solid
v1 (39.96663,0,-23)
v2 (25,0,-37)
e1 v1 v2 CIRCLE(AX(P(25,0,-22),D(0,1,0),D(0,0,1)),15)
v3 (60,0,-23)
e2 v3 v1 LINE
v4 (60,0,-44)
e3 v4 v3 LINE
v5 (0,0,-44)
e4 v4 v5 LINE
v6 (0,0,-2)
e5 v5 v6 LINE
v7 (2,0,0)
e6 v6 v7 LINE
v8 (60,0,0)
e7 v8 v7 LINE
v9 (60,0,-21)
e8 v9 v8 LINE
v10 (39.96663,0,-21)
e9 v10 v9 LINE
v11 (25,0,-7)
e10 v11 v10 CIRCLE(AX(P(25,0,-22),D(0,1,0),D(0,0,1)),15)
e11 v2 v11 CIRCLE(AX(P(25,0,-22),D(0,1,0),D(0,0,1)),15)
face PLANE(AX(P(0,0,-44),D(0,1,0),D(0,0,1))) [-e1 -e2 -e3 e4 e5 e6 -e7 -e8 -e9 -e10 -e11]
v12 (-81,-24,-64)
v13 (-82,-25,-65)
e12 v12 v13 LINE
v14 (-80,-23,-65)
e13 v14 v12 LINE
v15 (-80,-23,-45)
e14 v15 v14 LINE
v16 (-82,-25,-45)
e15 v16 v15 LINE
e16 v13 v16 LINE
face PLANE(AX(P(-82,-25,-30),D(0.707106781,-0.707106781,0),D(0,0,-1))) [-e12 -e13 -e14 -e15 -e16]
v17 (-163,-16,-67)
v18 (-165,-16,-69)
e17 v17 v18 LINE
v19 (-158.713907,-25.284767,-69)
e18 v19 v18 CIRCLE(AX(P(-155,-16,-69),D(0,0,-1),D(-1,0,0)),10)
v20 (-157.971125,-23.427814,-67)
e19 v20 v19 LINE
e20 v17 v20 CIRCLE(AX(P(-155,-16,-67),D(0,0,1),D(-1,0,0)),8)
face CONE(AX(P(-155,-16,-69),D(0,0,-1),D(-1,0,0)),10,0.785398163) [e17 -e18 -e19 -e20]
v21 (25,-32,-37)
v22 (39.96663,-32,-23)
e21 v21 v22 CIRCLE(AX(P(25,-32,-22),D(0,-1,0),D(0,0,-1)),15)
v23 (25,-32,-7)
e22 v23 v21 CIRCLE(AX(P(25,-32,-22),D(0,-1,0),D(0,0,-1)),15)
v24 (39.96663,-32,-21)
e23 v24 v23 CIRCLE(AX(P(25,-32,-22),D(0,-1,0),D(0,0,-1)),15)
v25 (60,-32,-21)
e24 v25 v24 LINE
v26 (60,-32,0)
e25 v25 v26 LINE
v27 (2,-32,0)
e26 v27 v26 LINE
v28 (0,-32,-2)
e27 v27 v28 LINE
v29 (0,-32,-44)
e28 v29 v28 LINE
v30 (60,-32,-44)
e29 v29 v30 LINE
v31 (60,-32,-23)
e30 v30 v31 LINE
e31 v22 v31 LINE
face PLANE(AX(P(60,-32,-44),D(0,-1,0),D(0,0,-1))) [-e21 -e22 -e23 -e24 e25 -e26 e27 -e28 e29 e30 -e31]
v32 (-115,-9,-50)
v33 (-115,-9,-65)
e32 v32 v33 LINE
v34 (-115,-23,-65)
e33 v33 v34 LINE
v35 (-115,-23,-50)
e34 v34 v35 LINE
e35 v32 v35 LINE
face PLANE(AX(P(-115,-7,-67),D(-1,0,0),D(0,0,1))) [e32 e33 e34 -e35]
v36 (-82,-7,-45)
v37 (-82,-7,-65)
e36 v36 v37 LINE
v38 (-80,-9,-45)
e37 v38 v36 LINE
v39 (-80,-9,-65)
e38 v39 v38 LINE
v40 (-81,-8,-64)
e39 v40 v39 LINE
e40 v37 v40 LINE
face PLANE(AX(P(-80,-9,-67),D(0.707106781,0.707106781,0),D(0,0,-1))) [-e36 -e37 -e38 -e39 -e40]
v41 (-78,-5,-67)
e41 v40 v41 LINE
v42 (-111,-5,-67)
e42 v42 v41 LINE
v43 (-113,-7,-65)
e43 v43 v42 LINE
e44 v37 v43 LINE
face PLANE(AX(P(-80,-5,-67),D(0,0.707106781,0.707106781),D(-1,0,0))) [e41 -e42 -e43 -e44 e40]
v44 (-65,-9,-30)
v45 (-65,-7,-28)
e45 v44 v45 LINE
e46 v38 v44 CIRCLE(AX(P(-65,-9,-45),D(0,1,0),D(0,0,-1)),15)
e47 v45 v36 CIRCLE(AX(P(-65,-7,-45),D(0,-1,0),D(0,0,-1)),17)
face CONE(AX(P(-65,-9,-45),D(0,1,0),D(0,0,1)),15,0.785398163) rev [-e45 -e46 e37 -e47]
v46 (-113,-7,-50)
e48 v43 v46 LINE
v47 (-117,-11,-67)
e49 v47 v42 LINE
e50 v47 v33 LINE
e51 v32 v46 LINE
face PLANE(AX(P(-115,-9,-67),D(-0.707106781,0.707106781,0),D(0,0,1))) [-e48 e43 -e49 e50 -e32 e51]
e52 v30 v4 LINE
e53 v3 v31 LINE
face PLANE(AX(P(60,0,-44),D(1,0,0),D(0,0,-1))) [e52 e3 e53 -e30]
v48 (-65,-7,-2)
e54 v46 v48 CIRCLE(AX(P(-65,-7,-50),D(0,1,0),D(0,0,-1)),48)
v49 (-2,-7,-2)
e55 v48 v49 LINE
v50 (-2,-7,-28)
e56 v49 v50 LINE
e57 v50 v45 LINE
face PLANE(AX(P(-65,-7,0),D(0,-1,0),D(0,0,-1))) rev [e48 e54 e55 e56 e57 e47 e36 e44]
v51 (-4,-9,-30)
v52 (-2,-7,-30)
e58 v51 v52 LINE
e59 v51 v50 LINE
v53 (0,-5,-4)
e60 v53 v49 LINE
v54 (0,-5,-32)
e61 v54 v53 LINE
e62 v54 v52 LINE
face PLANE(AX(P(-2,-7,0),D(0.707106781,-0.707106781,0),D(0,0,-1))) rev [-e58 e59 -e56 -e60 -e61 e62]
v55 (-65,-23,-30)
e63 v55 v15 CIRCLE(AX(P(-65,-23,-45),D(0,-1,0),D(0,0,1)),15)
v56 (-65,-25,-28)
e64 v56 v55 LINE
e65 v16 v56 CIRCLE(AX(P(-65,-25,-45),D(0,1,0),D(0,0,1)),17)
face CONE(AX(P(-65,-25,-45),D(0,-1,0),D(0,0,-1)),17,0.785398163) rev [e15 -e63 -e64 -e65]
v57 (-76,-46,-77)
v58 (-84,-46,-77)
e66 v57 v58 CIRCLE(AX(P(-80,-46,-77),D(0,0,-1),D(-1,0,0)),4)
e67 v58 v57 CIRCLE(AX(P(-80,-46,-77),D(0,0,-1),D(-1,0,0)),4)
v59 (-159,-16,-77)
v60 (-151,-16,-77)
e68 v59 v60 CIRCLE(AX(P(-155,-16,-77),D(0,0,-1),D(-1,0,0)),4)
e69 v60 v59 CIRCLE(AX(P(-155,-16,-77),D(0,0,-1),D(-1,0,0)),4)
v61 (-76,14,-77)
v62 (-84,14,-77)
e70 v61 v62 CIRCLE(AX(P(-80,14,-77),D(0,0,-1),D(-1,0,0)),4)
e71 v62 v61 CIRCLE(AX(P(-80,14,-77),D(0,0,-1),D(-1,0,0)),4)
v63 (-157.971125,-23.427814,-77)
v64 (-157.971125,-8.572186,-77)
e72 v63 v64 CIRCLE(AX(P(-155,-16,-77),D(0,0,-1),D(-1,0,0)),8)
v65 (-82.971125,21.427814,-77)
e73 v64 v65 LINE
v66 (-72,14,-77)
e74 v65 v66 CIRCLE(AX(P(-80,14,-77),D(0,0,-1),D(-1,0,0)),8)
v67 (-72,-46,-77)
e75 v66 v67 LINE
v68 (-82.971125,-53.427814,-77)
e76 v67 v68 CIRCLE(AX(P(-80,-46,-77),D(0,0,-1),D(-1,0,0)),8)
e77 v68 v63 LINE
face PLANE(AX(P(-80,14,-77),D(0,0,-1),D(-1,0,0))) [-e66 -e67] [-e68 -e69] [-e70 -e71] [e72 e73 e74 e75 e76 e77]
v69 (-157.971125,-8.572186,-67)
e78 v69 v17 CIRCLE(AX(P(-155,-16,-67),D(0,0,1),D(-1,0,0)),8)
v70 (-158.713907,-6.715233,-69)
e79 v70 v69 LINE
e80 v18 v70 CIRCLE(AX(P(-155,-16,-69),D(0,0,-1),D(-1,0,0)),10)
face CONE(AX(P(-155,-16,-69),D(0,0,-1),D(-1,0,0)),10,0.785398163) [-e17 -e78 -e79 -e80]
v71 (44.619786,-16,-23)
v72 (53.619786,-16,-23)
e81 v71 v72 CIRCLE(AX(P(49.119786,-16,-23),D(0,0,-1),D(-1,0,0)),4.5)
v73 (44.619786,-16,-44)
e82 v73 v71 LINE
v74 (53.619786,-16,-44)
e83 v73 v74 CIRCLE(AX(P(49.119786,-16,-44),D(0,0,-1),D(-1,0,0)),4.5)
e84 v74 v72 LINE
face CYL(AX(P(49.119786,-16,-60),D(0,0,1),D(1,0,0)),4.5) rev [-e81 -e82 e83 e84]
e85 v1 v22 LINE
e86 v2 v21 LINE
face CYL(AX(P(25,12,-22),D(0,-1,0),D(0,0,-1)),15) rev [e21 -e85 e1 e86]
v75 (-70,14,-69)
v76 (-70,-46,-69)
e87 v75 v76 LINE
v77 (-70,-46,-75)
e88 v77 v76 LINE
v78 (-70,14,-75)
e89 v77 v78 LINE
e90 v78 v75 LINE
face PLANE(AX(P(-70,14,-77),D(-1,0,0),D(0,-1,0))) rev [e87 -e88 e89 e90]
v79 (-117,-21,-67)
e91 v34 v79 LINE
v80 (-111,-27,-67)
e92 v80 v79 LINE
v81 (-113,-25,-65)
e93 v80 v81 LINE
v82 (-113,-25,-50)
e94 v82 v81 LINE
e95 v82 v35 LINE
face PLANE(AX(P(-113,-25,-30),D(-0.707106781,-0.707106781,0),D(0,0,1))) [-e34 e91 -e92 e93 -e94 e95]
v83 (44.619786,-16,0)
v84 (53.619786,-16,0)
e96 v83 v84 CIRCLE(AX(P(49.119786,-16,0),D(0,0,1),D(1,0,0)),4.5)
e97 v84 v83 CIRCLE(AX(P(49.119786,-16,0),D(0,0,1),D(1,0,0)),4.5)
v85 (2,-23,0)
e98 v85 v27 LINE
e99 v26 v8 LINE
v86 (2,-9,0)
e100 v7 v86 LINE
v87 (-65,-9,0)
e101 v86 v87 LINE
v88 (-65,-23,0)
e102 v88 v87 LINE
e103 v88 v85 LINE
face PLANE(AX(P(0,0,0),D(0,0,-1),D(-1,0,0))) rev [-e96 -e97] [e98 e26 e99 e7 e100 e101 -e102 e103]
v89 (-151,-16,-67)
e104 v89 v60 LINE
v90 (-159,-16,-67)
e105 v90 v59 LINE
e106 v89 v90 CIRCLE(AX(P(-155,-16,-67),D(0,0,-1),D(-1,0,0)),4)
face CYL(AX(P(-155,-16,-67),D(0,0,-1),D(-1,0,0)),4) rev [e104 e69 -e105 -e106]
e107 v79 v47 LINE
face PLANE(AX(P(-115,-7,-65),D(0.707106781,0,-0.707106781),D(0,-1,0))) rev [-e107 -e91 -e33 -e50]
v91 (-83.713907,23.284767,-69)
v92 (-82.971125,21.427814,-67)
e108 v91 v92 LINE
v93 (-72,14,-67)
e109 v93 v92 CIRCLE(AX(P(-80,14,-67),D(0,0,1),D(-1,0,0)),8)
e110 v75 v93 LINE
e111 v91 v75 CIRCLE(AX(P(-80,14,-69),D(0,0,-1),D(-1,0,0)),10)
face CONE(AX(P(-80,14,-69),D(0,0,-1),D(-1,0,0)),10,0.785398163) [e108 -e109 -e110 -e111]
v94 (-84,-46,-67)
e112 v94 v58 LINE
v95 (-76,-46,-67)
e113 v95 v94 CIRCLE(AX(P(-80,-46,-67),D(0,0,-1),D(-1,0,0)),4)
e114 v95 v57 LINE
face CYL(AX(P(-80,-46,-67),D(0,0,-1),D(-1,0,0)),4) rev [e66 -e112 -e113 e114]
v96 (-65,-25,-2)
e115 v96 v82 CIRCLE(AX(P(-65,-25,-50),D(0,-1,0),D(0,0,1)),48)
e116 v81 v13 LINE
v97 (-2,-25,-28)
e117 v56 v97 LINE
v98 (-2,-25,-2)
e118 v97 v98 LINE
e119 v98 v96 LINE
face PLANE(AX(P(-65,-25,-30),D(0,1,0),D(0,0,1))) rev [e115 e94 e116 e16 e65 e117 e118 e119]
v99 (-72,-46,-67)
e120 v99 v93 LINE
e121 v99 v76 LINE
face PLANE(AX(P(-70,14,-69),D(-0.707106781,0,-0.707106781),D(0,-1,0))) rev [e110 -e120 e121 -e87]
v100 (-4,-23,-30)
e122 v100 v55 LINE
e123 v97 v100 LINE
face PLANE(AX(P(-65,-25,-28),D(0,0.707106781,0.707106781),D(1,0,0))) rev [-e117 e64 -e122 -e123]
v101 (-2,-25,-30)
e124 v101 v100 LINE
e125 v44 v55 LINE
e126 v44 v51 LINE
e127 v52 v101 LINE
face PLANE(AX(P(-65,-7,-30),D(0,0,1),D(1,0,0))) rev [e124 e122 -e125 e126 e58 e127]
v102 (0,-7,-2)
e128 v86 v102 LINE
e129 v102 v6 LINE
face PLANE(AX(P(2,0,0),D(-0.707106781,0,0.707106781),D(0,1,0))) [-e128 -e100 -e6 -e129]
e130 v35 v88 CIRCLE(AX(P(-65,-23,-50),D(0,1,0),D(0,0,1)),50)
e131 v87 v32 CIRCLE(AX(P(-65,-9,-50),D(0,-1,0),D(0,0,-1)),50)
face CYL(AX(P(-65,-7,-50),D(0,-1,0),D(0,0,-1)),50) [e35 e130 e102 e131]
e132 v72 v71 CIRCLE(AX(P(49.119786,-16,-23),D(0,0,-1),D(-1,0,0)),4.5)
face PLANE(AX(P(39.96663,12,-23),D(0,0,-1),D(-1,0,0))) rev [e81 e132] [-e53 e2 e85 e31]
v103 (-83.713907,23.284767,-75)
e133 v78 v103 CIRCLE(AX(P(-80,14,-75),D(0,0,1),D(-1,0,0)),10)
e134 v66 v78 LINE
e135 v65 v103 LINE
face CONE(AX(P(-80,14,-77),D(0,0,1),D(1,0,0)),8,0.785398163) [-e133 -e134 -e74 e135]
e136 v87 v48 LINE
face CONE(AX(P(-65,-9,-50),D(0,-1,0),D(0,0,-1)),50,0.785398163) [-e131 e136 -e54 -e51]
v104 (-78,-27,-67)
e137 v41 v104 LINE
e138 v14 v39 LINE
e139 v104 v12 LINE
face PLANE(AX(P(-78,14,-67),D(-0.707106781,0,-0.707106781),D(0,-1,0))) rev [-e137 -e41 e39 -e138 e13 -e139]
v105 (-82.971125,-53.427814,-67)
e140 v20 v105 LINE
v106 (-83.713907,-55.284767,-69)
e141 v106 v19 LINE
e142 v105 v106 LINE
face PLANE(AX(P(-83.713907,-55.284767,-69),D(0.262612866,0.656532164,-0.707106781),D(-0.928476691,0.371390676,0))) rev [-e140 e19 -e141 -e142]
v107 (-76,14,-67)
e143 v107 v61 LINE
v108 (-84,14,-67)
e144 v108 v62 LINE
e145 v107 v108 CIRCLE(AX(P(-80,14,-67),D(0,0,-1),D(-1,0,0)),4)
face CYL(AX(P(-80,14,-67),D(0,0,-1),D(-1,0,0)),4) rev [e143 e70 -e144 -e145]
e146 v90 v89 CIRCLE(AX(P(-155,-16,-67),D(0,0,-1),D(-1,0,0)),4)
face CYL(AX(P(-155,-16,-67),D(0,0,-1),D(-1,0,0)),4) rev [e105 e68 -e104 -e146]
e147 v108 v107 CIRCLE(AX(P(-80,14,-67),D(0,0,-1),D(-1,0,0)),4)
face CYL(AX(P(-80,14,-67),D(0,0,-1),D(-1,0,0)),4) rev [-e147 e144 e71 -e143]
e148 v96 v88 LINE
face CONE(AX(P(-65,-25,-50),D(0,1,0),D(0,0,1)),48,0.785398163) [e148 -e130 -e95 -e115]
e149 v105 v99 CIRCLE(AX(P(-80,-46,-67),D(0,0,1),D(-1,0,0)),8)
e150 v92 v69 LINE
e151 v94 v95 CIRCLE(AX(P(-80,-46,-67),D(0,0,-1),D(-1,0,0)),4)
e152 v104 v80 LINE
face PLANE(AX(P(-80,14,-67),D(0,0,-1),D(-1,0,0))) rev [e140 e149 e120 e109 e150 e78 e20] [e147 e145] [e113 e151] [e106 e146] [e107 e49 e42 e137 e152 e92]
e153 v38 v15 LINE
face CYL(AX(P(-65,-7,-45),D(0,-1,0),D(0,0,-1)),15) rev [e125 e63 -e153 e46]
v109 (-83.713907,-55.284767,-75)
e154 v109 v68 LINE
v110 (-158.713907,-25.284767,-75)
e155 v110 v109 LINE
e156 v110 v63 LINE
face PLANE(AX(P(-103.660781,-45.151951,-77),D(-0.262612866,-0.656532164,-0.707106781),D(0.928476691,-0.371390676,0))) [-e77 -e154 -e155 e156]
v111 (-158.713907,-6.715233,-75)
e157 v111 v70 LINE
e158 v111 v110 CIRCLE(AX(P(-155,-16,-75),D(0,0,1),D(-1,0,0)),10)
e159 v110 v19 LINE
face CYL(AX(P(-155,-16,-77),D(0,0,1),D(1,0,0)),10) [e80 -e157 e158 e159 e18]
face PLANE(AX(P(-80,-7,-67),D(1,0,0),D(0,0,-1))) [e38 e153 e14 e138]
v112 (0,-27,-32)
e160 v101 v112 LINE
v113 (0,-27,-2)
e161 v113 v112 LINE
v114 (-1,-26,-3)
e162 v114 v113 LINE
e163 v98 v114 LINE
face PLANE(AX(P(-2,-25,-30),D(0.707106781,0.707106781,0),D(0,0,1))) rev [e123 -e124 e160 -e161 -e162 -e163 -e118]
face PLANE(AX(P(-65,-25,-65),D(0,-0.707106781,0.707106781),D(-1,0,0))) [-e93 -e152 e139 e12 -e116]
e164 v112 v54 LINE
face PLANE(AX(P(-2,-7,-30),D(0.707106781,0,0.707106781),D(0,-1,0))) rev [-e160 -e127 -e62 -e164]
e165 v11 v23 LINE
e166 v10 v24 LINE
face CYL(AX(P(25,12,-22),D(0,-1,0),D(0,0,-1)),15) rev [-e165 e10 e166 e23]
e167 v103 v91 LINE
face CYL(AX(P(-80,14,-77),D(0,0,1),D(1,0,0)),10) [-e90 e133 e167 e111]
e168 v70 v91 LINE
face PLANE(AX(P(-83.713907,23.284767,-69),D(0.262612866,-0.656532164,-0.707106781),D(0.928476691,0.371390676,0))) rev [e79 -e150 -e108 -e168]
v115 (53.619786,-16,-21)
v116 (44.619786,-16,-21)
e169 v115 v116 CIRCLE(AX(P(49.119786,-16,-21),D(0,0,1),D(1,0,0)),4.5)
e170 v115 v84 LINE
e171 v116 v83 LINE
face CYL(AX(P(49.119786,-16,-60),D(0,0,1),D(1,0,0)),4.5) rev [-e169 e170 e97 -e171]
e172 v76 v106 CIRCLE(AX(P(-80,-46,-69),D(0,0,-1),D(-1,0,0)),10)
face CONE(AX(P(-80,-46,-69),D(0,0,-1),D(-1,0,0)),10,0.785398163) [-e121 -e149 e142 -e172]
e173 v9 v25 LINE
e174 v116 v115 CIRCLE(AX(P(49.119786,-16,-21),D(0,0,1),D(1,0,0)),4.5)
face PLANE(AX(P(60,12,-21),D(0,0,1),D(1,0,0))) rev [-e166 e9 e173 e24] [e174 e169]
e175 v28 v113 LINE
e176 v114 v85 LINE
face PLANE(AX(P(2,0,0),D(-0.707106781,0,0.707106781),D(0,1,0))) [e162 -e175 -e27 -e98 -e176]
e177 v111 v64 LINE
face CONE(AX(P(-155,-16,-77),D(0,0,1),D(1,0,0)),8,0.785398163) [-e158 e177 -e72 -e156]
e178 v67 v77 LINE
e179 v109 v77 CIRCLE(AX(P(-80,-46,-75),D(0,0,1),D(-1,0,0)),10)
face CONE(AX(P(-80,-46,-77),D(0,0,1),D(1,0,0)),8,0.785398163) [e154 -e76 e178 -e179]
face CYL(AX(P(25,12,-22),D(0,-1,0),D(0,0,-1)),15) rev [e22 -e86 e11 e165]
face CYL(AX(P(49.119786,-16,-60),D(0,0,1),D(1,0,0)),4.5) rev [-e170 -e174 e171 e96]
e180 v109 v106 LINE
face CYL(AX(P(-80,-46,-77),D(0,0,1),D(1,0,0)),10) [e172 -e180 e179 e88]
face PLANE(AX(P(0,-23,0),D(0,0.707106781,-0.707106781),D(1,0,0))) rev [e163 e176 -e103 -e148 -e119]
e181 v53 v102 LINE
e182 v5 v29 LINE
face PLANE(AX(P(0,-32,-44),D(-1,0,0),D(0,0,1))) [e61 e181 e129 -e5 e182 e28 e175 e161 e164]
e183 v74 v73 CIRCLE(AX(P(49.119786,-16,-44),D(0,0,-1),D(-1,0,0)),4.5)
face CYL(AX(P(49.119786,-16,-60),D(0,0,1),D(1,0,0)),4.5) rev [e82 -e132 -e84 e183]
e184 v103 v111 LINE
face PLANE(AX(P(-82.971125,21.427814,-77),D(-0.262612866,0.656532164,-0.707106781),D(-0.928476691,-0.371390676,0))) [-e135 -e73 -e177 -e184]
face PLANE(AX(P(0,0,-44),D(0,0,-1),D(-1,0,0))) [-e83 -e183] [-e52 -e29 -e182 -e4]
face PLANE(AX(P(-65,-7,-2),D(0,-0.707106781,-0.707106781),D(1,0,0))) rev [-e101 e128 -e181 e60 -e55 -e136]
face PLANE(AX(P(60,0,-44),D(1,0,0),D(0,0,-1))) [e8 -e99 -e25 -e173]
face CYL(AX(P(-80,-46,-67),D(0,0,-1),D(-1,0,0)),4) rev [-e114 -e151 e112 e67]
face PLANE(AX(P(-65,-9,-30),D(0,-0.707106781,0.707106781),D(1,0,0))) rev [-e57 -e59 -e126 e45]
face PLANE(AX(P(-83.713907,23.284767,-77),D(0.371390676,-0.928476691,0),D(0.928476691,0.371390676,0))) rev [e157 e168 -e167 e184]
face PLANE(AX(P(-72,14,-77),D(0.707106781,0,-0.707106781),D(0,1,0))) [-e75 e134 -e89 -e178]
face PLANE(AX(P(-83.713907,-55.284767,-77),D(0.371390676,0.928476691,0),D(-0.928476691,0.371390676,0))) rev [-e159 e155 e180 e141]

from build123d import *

# Parameters (mm, degrees)
CLAMP_BLOCK_SKETCH_W       = 60
CLAMP_BLOCK_SKETCH_H       = 32
CLAMP_BLOCK_DEPTH          = 44
SPLIT_BORE_CUT_DEPTH       = 44
CLAMP_BOLT_HOLE_SKETCH_R   = 4.5
CLAMP_BOLT_HOLE_DEPTH      = 60
ARM_SKETCH_W               = 30
ARM_SKETCH_H               = 18
ARM_DEPTH                  = 65
ARM_BEND_DEPTH             = 18
MOUNTING_FLANGE_DEPTH      = 10
FLANGE_HOLES_SKETCH_R      = 4
FLANGE_HOLES_3X_8_DEPTH    = 10
ARM_BEND_CHAMFER_SIZE      = 2
CLAMP_BLOCK_CHAMFER_A_SIZE = 2
ARM_CLAMP_CHAMFER_A_SIZE   = 2
ARM_EDGE_CHAMFER_SIZE      = 2
ARM_CLAMP_CHAMFER_B_SIZE   = 2
CLAMP_BLOCK_CHAMFER_B_SIZE = 2
ARM_FLANGE_CHAMFER_A_SIZE  = 2
BEND_FLANGE_CHAMFER_A_SIZE = 2
ARM_FLANGE_CHAMFER_B_SIZE  = 2
BEND_FLANGE_CHAMFER_B_SIZE = 2
FLANGE_EDGE_CHAMFER_SIZE   = 2
BEND_EDGE_CHAMFER_A_SIZE   = 2
BEND_EDGE_CHAMFER_B_SIZE   = 2
ARM_CLAMP_CHAMFER_C_SIZE   = 2


with BuildPart() as part:
    # Clamp Block Sketch → Clamp Block (new body)
    with BuildSketch(Plane.XY):
        with Locations((30, -16)):
            Rectangle(CLAMP_BLOCK_SKETCH_W, CLAMP_BLOCK_SKETCH_H)
    extrude(amount=-CLAMP_BLOCK_DEPTH)

    # Split Bore Sketch → Split Bore Cut (cut)
    with BuildSketch(Plane.XZ.offset(32)):
        with BuildLine():
            Line((60, -21), (60, -23))
            Line((60, -23), (39.966629547, -23))
            ThreePointArc((39.966629547, -23), (10, -22), (39.966629547, -21))
            Line((39.966629547, -21), (60, -21))
        make_face()
    extrude(amount=-SPLIT_BORE_CUT_DEPTH, mode=Mode.SUBTRACT)

    # Clamp Bolt Hole Sketch → Clamp Bolt Hole (cut)
    with BuildSketch(Plane.XY):
        with Locations(Location((49.119785918, -16, 0), (0, 0, 180))):
            Circle(CLAMP_BOLT_HOLE_SKETCH_R)
    extrude(amount=-CLAMP_BOLT_HOLE_DEPTH, mode=Mode.SUBTRACT)

    # Arm Sketch → Arm (add)
    with BuildSketch(Plane.ZY):
        with Locations((-15, -16)):
            Rectangle(ARM_SKETCH_W, ARM_SKETCH_H)
    extrude(amount=ARM_DEPTH)

    # Arm Bend Sketch → Arm Bend (add)
    with BuildSketch(Plane.XZ.offset(25)):
        with BuildLine():
            Line((-115, -67), (-80, -67))
            Line((-80, -67), (-80, -45))
            ThreePointArc((-80, -45), (-75.606601718, -34.393398282), (-65, -30))
            Line((-65, -30), (-65, 0))
            ThreePointArc((-65, 0), (-100.355339059, -14.644660941), (-115, -50))
            Line((-115, -50), (-115, -67))
        make_face()
    extrude(amount=-ARM_BEND_DEPTH)

    # Mounting Flange Sketch → Mounting Flange (add)
    with BuildSketch(Plane(origin=(0, 0, -67), x_dir=(-1, 0, 0), z_dir=(0, 0, -1))):
        with BuildLine():
            Line((83.713906764, 23.284766909), (158.713906764, -6.715233091))
            ThreePointArc((158.713906764, -6.715233091), (165, -16), (158.713906764, -25.284766909))
            Line((158.713906764, -25.284766909), (83.713906764, -55.284766909))
            ThreePointArc((83.713906764, -55.284766909), (74.393711907, -54.280672305), (70, -46))
            Line((70, -46), (70, 14))
            ThreePointArc((70, 14), (74.393711907, 22.280672305), (83.713906764, 23.284766909))
        make_face()
    extrude(amount=MOUNTING_FLANGE_DEPTH)

    # Flange Holes Sketch → Flange Holes 3xØ8 (cut)
    with BuildSketch(Plane(origin=(0, 0, -77), x_dir=(-1, 0, 0), z_dir=(0, 0, -1))):
        with Locations((80, 14)):
            Circle(FLANGE_HOLES_SKETCH_R)
        with Locations((155, -16)):
            Circle(FLANGE_HOLES_SKETCH_R)
        with Locations((80, -46)):
            Circle(FLANGE_HOLES_SKETCH_R)
    extrude(amount=-FLANGE_HOLES_3X_8_DEPTH, mode=Mode.SUBTRACT)

    # Arm-Bend Chamfer
    arm_bend_chamfer_edges = [part.edges().sort_by_distance(p)[0] for p in [
        (-32.5, -25, 0),
        (-100.355339059, -25, -14.644660941),
        (-115, -25, -58.5),
    ]]
    chamfer(arm_bend_chamfer_edges, length=ARM_BEND_CHAMFER_SIZE)

    # Clamp Block Chamfer A
    clamp_block_chamfer_a_edges = [part.edges().sort_by_distance(p)[0] for p in [
        (0, -27.5, 0),
    ]]
    chamfer(clamp_block_chamfer_a_edges, length=CLAMP_BLOCK_CHAMFER_A_SIZE)

    # Arm-Clamp Chamfer A
    arm_clamp_chamfer_a_edges = [part.edges().sort_by_distance(p)[0] for p in [
        (0, -25, -16),
    ]]
    chamfer(arm_clamp_chamfer_a_edges, length=ARM_CLAMP_CHAMFER_A_SIZE)

    # Arm Edge Chamfer
    arm_edge_chamfer_edges = [part.edges().sort_by_distance(p)[0] for p in [
        (-32.5, -7, 0),
        (-115, -7, -58.5),
        (-100.355339059, -7, -14.644660941),
    ]]
    chamfer(arm_edge_chamfer_edges, length=ARM_EDGE_CHAMFER_SIZE)

    # Arm-Clamp Chamfer B
    arm_clamp_chamfer_b_edges = [part.edges().sort_by_distance(p)[0] for p in [
        (0, -7, -16),
    ]]
    chamfer(arm_clamp_chamfer_b_edges, length=ARM_CLAMP_CHAMFER_B_SIZE)

    # Clamp Block Chamfer B
    clamp_block_chamfer_b_edges = [part.edges().sort_by_distance(p)[0] for p in [
        (0, -4.5, 0),
    ]]
    chamfer(clamp_block_chamfer_b_edges, length=CLAMP_BLOCK_CHAMFER_B_SIZE)

    # Arm-Flange Chamfer A
    arm_flange_chamfer_a_edges = [part.edges().sort_by_distance(p)[0] for p in [
        (-96.5, -25, -67),
        (-74.393711907, 22.280672305, -67),
        (-70, -16, -67),
        (-74.393711907, -54.280672305, -67),
        (-121.213906764, -40.284766909, -67),
        (-165, -16, -67),
        (-121.213906764, 8.284766909, -67),
    ]]
    chamfer(arm_flange_chamfer_a_edges, length=ARM_FLANGE_CHAMFER_A_SIZE)

    # Bend-Flange Chamfer A
    bend_flange_chamfer_a_edges = [part.edges().sort_by_distance(p)[0] for p in [
        (-115, -16, -67),
    ]]
    chamfer(bend_flange_chamfer_a_edges, length=BEND_FLANGE_CHAMFER_A_SIZE)

    # Arm-Flange Chamfer B
    arm_flange_chamfer_b_edges = [part.edges().sort_by_distance(p)[0] for p in [
        (-96.5, -7, -67),
    ]]
    chamfer(arm_flange_chamfer_b_edges, length=ARM_FLANGE_CHAMFER_B_SIZE)

    # Bend-Flange Chamfer B
    bend_flange_chamfer_b_edges = [part.edges().sort_by_distance(p)[0] for p in [
        (-80, -16, -67),
    ]]
    chamfer(bend_flange_chamfer_b_edges, length=BEND_FLANGE_CHAMFER_B_SIZE)

    # Flange Edge Chamfer
    flange_edge_chamfer_edges = [part.edges().sort_by_distance(p)[0] for p in [
        (-74.393711907, 22.280672305, -77),
        (-70, -16, -77),
        (-74.393711907, -54.280672305, -77),
        (-121.213906764, -40.284766909, -77),
        (-165, -16, -77),
        (-121.213906764, 8.284766909, -77),
    ]]
    chamfer(flange_edge_chamfer_edges, length=FLANGE_EDGE_CHAMFER_SIZE)

    # Bend Edge Chamfer A
    bend_edge_chamfer_a_edges = [part.edges().sort_by_distance(p)[0] for p in [
        (-80, -25, -55),
        (-33.5, -25, -30),
        (-75.606601718, -25, -34.393398282),
    ]]
    chamfer(bend_edge_chamfer_a_edges, length=BEND_EDGE_CHAMFER_A_SIZE)

    # Bend Edge Chamfer B
    bend_edge_chamfer_b_edges = [part.edges().sort_by_distance(p)[0] for p in [
        (-80, -7, -55),
        (-33.5, -7, -30),
        (-75.606601718, -7, -34.393398282),
    ]]
    chamfer(bend_edge_chamfer_b_edges, length=BEND_EDGE_CHAMFER_B_SIZE)

    # Arm-Clamp Chamfer C
    arm_clamp_chamfer_c_edges = [part.edges().sort_by_distance(p)[0] for p in [
        (0, -16, -30),
    ]]
    chamfer(arm_clamp_chamfer_c_edges, length=ARM_CLAMP_CHAMFER_C_SIZE)


solid = part.part
